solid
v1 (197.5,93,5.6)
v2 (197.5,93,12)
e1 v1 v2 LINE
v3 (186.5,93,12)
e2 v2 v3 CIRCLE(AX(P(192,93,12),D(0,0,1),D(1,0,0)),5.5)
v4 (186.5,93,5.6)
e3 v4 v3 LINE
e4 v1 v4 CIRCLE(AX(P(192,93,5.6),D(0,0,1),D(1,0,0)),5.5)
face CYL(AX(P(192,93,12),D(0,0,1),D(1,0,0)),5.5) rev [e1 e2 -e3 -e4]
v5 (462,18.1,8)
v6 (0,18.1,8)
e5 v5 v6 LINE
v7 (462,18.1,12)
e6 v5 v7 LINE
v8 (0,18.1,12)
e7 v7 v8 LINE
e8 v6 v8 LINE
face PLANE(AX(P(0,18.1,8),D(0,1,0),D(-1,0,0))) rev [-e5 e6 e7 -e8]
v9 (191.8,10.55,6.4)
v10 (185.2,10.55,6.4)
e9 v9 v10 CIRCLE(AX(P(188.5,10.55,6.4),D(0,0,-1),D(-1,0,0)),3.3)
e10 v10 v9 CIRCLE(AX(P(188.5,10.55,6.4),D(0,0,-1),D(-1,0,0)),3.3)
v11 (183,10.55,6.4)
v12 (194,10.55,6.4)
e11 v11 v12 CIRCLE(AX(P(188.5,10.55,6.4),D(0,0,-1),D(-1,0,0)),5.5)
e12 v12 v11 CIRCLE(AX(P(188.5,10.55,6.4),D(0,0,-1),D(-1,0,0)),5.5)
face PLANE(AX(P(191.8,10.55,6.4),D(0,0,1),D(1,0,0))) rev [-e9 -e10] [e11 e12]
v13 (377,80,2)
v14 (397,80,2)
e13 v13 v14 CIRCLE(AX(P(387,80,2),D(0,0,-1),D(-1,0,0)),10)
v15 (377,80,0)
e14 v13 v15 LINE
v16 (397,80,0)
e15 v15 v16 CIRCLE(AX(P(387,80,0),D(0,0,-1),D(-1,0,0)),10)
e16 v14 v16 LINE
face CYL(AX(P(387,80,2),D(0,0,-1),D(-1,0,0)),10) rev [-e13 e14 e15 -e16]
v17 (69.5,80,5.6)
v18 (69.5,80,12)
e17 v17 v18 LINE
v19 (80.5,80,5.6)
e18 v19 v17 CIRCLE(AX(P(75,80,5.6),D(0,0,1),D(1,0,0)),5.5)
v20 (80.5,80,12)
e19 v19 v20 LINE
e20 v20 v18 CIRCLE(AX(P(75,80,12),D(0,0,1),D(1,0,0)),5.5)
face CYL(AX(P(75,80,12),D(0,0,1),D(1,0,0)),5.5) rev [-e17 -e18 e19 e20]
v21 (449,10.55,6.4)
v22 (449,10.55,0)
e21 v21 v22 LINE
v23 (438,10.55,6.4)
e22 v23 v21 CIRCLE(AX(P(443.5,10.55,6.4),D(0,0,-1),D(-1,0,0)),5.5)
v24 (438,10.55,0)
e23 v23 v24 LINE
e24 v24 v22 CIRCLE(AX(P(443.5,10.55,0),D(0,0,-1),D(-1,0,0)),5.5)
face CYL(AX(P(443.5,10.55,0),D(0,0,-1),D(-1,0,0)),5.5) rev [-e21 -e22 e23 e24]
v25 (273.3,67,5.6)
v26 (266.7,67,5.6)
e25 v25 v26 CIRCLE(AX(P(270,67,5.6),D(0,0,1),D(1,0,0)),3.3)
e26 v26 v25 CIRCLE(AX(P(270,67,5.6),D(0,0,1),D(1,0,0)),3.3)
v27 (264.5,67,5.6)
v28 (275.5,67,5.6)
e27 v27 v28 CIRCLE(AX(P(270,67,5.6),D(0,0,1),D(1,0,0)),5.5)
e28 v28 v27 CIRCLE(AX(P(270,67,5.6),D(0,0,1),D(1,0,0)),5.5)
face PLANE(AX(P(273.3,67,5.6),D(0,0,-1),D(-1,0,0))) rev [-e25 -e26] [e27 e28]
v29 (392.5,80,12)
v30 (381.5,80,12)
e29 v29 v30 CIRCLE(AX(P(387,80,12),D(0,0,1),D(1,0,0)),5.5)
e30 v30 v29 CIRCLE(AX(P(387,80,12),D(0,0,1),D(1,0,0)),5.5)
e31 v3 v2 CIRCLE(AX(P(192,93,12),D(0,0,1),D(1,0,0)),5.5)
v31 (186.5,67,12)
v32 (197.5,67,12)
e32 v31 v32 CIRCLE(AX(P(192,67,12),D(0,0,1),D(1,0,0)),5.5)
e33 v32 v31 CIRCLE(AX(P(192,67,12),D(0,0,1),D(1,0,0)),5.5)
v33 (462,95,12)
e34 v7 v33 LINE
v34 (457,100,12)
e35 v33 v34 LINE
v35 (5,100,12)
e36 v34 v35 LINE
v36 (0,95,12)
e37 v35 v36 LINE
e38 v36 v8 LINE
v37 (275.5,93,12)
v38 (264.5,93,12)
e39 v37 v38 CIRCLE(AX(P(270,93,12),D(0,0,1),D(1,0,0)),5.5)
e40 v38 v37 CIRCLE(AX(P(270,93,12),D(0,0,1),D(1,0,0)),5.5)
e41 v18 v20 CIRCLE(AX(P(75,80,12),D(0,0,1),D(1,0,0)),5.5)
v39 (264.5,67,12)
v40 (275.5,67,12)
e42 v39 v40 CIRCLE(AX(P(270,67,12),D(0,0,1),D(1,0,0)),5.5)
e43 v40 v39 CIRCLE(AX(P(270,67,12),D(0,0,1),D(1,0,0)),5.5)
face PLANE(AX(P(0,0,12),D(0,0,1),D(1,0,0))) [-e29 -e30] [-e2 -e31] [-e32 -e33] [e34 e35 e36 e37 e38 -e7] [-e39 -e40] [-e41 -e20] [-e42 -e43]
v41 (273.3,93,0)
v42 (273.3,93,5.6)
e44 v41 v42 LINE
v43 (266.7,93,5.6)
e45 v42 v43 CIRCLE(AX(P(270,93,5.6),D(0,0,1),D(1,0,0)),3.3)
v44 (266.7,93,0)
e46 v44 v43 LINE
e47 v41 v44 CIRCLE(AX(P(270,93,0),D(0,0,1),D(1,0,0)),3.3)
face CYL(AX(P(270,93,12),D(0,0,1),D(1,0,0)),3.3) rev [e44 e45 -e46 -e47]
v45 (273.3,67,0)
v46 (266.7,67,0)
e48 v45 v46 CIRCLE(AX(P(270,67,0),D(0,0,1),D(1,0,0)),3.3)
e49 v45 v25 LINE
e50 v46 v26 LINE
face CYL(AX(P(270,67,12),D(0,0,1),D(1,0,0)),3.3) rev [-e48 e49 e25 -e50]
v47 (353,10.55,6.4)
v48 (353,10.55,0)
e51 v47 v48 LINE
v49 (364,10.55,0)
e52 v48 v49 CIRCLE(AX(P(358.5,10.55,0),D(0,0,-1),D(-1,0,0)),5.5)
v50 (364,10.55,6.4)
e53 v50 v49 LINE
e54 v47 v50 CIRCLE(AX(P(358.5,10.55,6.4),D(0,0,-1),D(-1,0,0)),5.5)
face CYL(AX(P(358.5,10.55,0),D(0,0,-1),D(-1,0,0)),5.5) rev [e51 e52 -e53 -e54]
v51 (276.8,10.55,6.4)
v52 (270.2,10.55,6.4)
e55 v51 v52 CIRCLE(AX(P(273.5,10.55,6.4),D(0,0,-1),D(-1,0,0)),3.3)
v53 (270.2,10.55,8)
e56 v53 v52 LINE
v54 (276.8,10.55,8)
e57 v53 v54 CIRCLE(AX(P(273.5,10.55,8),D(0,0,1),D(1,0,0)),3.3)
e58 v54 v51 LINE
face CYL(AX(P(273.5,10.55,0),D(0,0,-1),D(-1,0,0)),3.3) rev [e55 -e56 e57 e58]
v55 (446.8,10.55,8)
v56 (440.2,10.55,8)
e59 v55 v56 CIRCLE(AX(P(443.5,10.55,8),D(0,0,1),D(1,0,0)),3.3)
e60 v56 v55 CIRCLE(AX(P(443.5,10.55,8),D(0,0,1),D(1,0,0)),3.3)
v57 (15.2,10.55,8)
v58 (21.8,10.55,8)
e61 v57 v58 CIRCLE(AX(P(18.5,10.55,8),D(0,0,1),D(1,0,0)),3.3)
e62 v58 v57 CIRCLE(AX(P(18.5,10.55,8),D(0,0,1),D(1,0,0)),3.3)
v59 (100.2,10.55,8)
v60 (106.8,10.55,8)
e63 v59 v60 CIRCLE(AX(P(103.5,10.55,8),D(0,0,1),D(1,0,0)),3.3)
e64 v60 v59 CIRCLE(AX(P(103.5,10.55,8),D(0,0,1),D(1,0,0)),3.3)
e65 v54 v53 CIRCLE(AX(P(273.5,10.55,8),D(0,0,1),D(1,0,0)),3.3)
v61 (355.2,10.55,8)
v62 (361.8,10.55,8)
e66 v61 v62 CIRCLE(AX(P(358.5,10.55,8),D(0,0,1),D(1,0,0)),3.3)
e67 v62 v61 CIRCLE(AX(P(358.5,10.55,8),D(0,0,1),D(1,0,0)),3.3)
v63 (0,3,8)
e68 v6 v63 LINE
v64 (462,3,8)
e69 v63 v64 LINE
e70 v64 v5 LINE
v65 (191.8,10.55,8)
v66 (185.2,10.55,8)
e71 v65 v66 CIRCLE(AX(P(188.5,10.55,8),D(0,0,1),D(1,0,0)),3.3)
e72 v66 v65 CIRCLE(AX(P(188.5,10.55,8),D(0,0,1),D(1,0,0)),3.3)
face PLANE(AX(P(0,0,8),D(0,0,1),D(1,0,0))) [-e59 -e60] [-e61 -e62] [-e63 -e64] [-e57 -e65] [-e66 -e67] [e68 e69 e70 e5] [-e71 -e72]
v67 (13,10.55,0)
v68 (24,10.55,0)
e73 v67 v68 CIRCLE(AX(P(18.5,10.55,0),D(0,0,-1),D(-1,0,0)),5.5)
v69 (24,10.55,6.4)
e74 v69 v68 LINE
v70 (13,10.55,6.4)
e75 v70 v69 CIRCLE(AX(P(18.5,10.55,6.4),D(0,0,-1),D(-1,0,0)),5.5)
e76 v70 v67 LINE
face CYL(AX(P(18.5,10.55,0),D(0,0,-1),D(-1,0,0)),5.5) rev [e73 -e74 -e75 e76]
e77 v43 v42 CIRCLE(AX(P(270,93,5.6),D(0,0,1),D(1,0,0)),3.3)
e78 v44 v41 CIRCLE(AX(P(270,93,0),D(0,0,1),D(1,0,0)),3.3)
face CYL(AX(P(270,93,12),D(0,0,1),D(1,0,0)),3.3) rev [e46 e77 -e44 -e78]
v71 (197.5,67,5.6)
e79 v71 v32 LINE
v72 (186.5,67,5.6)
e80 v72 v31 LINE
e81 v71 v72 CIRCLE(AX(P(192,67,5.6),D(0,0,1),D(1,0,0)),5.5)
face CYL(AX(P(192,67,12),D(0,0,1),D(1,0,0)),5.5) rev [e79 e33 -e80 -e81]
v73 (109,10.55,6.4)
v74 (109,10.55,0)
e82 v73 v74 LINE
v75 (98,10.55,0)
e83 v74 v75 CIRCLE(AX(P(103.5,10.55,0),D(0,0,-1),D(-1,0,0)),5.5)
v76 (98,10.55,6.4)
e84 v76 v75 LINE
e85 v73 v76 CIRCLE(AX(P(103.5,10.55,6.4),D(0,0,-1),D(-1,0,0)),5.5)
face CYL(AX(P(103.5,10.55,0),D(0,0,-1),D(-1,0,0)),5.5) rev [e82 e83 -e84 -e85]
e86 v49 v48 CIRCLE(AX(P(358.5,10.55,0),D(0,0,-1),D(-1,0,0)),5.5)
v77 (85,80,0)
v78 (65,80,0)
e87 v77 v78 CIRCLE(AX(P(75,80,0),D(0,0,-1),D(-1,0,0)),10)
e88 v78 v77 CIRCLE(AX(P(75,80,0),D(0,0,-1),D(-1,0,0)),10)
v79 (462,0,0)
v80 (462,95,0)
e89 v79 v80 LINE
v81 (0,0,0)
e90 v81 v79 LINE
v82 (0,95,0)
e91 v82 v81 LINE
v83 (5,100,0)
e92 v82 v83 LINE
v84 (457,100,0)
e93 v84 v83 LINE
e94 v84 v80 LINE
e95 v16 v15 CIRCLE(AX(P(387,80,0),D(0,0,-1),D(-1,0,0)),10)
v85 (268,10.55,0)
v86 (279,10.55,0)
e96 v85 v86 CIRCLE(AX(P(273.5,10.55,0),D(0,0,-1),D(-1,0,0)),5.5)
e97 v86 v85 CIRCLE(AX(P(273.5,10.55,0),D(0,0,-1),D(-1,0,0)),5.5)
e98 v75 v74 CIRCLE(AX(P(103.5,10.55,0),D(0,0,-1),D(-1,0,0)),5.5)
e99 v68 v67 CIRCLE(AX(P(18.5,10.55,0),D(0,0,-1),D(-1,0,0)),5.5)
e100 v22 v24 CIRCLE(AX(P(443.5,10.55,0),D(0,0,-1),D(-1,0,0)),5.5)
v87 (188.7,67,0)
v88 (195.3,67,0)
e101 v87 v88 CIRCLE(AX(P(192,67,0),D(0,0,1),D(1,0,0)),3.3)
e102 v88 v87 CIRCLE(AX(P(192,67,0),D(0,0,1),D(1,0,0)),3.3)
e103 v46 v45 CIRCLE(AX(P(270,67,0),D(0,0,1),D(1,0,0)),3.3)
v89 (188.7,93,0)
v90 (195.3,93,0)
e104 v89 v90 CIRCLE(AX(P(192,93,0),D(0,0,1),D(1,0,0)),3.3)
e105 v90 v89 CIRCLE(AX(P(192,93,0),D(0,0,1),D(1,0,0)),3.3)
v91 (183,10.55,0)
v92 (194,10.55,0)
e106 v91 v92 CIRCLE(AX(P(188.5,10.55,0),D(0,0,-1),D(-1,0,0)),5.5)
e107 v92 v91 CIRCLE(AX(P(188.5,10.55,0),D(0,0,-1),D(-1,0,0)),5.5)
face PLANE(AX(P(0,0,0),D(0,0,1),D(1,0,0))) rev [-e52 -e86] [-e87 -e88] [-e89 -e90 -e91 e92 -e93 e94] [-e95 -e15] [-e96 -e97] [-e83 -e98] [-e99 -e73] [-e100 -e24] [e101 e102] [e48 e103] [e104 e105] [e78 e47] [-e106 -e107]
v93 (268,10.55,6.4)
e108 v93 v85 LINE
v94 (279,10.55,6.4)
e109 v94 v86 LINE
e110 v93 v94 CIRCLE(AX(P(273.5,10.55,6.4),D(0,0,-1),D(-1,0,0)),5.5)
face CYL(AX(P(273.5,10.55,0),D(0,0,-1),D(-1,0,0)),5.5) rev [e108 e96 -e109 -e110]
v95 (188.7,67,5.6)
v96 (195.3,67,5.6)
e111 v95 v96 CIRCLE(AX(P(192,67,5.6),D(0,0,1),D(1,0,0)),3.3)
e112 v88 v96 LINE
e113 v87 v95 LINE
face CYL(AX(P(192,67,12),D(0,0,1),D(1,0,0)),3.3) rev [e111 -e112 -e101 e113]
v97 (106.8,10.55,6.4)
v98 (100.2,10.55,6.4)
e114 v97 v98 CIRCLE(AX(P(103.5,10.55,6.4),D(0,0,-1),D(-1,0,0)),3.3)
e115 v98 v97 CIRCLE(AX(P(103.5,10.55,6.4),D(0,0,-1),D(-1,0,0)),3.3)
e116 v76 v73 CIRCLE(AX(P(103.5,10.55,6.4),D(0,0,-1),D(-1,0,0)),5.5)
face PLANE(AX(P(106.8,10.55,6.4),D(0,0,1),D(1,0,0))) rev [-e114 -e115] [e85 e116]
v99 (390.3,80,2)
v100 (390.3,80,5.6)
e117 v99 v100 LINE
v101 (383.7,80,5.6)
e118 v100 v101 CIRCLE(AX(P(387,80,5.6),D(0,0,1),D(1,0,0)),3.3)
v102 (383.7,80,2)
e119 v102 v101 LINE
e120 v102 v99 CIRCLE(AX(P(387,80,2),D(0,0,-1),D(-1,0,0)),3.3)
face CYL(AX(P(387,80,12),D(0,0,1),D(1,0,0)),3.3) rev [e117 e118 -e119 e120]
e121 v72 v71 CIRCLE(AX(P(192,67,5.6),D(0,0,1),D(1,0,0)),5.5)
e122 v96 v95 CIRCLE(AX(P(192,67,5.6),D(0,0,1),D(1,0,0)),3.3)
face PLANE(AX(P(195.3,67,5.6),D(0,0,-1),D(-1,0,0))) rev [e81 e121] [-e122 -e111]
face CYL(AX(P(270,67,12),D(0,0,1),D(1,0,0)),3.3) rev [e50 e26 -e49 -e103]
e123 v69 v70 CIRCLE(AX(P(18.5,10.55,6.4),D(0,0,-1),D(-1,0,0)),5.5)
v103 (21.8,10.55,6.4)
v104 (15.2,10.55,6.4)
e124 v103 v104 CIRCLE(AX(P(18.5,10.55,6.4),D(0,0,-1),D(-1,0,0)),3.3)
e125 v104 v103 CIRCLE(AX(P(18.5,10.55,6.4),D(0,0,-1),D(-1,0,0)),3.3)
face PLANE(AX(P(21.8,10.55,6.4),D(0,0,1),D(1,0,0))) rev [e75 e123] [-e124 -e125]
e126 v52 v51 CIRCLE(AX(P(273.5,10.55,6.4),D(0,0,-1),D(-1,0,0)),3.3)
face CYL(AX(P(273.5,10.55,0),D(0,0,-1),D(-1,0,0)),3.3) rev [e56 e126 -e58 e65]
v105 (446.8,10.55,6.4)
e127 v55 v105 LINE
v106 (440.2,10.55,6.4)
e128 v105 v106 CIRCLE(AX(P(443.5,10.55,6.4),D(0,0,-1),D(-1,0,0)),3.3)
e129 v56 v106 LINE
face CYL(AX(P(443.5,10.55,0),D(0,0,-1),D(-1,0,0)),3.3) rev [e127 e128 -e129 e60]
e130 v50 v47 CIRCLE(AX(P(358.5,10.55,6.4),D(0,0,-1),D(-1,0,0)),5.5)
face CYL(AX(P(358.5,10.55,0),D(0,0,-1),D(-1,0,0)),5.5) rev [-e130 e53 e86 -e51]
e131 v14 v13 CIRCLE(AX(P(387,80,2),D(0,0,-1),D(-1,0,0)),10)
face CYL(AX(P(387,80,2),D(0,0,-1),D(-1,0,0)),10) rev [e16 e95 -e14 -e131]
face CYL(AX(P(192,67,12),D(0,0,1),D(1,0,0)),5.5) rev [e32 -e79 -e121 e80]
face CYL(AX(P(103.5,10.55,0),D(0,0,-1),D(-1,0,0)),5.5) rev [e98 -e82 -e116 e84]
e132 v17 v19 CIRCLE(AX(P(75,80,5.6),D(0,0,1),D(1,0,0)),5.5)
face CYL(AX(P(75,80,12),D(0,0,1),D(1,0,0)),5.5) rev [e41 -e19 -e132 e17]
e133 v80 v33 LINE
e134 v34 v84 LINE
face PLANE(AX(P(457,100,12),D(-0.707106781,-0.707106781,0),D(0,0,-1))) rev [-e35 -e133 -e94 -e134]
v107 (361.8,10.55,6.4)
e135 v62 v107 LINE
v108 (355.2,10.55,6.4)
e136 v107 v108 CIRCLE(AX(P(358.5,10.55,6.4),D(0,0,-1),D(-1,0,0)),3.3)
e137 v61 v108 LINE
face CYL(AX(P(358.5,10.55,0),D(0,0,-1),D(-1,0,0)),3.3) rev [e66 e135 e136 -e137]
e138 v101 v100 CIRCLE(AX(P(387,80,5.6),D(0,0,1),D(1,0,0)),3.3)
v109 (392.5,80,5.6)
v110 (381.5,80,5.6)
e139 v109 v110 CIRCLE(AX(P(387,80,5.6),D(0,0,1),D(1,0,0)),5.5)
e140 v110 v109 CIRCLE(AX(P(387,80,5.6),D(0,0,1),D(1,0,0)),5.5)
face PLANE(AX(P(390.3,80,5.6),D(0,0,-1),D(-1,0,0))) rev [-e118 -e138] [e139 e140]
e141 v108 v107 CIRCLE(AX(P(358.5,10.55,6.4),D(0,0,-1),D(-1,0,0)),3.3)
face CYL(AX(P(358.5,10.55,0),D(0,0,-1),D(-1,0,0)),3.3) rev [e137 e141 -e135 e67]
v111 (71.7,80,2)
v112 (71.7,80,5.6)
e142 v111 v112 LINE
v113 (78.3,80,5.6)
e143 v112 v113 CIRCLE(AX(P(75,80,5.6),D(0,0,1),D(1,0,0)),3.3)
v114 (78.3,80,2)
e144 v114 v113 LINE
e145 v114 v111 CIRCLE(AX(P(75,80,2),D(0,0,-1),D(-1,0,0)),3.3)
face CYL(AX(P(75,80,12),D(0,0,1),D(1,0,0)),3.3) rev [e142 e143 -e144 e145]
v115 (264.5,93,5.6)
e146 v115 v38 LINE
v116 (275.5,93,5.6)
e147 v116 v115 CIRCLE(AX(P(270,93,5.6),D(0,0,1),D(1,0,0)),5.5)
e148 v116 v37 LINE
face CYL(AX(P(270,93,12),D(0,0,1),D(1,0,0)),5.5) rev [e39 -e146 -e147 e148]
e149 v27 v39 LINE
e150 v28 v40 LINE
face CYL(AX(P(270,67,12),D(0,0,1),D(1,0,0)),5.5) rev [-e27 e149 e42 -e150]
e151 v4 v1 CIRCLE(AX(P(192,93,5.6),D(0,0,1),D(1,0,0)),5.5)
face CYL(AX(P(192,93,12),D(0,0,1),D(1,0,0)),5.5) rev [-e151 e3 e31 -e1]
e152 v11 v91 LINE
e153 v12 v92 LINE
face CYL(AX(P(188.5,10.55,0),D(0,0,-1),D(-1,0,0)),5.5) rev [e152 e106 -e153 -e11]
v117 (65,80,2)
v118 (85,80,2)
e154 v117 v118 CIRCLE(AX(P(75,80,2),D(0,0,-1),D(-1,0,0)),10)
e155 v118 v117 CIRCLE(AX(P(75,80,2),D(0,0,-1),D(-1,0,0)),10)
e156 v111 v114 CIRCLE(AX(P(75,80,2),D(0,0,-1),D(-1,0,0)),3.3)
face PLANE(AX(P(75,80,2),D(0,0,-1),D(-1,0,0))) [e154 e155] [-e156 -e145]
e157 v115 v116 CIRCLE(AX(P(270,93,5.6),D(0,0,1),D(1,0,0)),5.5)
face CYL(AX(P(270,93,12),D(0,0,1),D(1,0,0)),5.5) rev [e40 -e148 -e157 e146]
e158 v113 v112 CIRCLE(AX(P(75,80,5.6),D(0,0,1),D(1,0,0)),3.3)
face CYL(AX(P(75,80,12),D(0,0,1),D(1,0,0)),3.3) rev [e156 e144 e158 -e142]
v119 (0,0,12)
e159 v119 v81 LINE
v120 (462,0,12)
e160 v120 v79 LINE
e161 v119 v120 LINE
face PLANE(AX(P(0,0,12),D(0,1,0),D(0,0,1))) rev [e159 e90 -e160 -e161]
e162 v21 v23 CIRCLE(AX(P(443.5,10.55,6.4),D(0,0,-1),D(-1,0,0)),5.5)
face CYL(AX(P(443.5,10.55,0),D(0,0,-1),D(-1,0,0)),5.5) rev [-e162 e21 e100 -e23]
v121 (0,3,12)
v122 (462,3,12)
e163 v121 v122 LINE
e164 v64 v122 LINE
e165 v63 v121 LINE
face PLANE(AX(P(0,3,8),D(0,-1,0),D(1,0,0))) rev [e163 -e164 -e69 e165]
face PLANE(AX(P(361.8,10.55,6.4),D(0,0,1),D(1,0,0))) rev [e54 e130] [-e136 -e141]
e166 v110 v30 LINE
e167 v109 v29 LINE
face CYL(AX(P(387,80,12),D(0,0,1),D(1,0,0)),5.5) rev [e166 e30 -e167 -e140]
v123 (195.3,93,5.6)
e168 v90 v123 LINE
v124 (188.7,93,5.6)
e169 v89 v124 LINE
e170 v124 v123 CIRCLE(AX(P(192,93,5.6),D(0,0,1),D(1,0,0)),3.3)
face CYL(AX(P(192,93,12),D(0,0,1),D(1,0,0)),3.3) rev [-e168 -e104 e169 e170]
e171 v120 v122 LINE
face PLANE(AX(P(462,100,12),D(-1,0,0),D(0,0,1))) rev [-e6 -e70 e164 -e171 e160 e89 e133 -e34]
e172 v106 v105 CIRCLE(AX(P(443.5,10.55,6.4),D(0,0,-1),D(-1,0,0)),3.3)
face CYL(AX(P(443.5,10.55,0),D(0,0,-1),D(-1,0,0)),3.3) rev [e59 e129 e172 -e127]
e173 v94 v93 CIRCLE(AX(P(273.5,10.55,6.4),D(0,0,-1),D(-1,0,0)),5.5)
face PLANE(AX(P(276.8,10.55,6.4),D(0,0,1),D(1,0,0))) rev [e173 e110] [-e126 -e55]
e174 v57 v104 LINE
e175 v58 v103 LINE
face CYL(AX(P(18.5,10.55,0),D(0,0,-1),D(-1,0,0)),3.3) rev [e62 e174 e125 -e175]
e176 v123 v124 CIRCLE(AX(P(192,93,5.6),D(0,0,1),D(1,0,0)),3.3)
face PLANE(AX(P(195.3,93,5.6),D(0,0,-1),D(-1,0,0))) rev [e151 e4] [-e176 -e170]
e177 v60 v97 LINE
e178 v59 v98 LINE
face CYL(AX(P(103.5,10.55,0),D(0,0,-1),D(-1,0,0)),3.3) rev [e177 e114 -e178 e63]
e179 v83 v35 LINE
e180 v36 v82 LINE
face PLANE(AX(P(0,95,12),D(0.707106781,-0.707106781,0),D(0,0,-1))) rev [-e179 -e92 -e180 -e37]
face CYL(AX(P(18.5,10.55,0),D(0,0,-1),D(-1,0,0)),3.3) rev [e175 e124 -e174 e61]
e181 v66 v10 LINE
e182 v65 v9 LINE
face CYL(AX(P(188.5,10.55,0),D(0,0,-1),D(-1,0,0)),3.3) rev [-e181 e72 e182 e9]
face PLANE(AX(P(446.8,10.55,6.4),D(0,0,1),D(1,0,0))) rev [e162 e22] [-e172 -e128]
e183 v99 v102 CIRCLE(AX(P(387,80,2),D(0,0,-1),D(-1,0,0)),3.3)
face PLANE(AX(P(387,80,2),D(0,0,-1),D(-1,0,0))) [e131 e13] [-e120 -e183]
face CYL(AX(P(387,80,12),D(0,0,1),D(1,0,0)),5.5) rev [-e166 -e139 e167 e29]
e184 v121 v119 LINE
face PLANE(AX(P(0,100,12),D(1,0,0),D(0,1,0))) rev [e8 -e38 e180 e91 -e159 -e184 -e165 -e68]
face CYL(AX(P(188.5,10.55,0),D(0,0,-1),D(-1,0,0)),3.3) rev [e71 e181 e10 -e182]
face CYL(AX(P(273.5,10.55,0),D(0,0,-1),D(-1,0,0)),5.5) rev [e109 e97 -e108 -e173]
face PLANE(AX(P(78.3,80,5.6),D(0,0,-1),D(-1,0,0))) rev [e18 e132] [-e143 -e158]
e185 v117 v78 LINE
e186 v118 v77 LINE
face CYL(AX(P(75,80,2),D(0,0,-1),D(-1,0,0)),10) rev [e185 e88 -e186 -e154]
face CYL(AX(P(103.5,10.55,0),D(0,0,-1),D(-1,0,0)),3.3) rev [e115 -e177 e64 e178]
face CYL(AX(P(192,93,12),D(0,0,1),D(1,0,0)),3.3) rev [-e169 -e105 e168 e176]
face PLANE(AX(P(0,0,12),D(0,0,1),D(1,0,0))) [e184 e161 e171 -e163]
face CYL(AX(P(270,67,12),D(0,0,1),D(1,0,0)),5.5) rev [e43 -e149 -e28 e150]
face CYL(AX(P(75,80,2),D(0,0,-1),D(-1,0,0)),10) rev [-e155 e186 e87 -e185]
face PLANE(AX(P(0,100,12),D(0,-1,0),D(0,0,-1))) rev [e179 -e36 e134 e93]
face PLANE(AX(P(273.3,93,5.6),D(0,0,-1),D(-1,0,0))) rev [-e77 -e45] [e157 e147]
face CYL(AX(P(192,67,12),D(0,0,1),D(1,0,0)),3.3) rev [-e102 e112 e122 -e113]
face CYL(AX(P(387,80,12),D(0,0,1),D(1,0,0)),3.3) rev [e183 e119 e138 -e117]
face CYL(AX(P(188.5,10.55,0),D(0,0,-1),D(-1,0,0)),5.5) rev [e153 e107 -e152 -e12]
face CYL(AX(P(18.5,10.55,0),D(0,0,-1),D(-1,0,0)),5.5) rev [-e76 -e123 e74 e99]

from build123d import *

# Parameters (mm, degrees)
SKETCH_1_W                   = 462
SKETCH_1_H                   = 100
EXTRUDE_1_DEPTH              = 12
SKETCH_2_W                   = 462
SKETCH_2_H                   = 15.1
CUT_EXTRUDE_1_DEPTH          = 4
HOLE_WIZARD_M6_1_D           = 6.6
HOLE_WIZARD_M6_1_CBORE_D     = 11
HOLE_WIZARD_M6_1_CBORE_DEPTH = 6.4
SKETCH_5_R                   = 10
CUT_EXTRUDE_2_DEPTH          = 2
HOLE_WIZARD_M6_2_D           = 6.6
HOLE_WIZARD_M6_2_CBORE_D     = 11
HOLE_WIZARD_M6_2_CBORE_DEPTH = 6.4
HOLE_WIZARD_M6_3_D           = 6.6
HOLE_WIZARD_M6_3_CBORE_D     = 11
HOLE_WIZARD_M6_3_CBORE_DEPTH = 6.4
CHAMFER_1_SIZE               = 5


with BuildPart() as part:
    # 草图1 → 凸台-拉伸1 (new body)
    with BuildSketch(Plane.XY):
        with Locations((231, 50)):
            Rectangle(SKETCH_1_W, SKETCH_1_H)
    extrude(amount=EXTRUDE_1_DEPTH)

    # 草图2 → 切除-拉伸1 (cut)
    with BuildSketch(Plane.XY.offset(12)):
        with Locations((231, 10.55)):
            Rectangle(SKETCH_2_W, SKETCH_2_H)
    extrude(amount=-CUT_EXTRUDE_1_DEPTH, mode=Mode.SUBTRACT)

    # M6 六角凹头螺钉的柱形沉头孔1 (through all)
    with Locations(Plane.XY.offset(12)):
        with Locations((192, 93), (270, 93), (192, 67), (270, 67)):
            CounterBoreHole(HOLE_WIZARD_M6_1_D / 2, HOLE_WIZARD_M6_1_CBORE_D / 2, HOLE_WIZARD_M6_1_CBORE_DEPTH)

    # 草图5 → 切除-拉伸2 (cut)
    with BuildSketch(Plane(origin=(0, 0, 0), x_dir=(-1, 0, 0), z_dir=(0, 0, -1))):
        with Locations((-387, 80)):
            Circle(SKETCH_5_R)
        with Locations((-75, 80)):
            Circle(SKETCH_5_R)
    extrude(amount=-CUT_EXTRUDE_2_DEPTH, mode=Mode.SUBTRACT)

    # M6 六角凹头螺钉的柱形沉头孔2 (through all)
    with Locations(Plane.XY.offset(12)):
        with Locations((75, 80), (387, 80)):
            CounterBoreHole(HOLE_WIZARD_M6_2_D / 2, HOLE_WIZARD_M6_2_CBORE_D / 2, HOLE_WIZARD_M6_2_CBORE_DEPTH)

    # M6 六角凹头螺钉的柱形沉头孔3 (through all)
    with Locations(Plane(origin=(0, 0, 0), x_dir=(-1, 0, 0), z_dir=(0, 0, -1))):
        with Locations((-443.5, 10.55), (-358.5, 10.55), (-273.5, 10.55), (-188.5, 10.55), (-103.5, 10.55), (-18.5, 10.55)):
            CounterBoreHole(HOLE_WIZARD_M6_3_D / 2, HOLE_WIZARD_M6_3_CBORE_D / 2, HOLE_WIZARD_M6_3_CBORE_DEPTH)

    # 倒角1
    chamfer_1_edges = [part.edges().sort_by_distance(p)[0] for p in [
        (0, 100, 6),
        (462, 100, 6),
    ]]
    chamfer(chamfer_1_edges, length=CHAMFER_1_SIZE)


solid = part.part
